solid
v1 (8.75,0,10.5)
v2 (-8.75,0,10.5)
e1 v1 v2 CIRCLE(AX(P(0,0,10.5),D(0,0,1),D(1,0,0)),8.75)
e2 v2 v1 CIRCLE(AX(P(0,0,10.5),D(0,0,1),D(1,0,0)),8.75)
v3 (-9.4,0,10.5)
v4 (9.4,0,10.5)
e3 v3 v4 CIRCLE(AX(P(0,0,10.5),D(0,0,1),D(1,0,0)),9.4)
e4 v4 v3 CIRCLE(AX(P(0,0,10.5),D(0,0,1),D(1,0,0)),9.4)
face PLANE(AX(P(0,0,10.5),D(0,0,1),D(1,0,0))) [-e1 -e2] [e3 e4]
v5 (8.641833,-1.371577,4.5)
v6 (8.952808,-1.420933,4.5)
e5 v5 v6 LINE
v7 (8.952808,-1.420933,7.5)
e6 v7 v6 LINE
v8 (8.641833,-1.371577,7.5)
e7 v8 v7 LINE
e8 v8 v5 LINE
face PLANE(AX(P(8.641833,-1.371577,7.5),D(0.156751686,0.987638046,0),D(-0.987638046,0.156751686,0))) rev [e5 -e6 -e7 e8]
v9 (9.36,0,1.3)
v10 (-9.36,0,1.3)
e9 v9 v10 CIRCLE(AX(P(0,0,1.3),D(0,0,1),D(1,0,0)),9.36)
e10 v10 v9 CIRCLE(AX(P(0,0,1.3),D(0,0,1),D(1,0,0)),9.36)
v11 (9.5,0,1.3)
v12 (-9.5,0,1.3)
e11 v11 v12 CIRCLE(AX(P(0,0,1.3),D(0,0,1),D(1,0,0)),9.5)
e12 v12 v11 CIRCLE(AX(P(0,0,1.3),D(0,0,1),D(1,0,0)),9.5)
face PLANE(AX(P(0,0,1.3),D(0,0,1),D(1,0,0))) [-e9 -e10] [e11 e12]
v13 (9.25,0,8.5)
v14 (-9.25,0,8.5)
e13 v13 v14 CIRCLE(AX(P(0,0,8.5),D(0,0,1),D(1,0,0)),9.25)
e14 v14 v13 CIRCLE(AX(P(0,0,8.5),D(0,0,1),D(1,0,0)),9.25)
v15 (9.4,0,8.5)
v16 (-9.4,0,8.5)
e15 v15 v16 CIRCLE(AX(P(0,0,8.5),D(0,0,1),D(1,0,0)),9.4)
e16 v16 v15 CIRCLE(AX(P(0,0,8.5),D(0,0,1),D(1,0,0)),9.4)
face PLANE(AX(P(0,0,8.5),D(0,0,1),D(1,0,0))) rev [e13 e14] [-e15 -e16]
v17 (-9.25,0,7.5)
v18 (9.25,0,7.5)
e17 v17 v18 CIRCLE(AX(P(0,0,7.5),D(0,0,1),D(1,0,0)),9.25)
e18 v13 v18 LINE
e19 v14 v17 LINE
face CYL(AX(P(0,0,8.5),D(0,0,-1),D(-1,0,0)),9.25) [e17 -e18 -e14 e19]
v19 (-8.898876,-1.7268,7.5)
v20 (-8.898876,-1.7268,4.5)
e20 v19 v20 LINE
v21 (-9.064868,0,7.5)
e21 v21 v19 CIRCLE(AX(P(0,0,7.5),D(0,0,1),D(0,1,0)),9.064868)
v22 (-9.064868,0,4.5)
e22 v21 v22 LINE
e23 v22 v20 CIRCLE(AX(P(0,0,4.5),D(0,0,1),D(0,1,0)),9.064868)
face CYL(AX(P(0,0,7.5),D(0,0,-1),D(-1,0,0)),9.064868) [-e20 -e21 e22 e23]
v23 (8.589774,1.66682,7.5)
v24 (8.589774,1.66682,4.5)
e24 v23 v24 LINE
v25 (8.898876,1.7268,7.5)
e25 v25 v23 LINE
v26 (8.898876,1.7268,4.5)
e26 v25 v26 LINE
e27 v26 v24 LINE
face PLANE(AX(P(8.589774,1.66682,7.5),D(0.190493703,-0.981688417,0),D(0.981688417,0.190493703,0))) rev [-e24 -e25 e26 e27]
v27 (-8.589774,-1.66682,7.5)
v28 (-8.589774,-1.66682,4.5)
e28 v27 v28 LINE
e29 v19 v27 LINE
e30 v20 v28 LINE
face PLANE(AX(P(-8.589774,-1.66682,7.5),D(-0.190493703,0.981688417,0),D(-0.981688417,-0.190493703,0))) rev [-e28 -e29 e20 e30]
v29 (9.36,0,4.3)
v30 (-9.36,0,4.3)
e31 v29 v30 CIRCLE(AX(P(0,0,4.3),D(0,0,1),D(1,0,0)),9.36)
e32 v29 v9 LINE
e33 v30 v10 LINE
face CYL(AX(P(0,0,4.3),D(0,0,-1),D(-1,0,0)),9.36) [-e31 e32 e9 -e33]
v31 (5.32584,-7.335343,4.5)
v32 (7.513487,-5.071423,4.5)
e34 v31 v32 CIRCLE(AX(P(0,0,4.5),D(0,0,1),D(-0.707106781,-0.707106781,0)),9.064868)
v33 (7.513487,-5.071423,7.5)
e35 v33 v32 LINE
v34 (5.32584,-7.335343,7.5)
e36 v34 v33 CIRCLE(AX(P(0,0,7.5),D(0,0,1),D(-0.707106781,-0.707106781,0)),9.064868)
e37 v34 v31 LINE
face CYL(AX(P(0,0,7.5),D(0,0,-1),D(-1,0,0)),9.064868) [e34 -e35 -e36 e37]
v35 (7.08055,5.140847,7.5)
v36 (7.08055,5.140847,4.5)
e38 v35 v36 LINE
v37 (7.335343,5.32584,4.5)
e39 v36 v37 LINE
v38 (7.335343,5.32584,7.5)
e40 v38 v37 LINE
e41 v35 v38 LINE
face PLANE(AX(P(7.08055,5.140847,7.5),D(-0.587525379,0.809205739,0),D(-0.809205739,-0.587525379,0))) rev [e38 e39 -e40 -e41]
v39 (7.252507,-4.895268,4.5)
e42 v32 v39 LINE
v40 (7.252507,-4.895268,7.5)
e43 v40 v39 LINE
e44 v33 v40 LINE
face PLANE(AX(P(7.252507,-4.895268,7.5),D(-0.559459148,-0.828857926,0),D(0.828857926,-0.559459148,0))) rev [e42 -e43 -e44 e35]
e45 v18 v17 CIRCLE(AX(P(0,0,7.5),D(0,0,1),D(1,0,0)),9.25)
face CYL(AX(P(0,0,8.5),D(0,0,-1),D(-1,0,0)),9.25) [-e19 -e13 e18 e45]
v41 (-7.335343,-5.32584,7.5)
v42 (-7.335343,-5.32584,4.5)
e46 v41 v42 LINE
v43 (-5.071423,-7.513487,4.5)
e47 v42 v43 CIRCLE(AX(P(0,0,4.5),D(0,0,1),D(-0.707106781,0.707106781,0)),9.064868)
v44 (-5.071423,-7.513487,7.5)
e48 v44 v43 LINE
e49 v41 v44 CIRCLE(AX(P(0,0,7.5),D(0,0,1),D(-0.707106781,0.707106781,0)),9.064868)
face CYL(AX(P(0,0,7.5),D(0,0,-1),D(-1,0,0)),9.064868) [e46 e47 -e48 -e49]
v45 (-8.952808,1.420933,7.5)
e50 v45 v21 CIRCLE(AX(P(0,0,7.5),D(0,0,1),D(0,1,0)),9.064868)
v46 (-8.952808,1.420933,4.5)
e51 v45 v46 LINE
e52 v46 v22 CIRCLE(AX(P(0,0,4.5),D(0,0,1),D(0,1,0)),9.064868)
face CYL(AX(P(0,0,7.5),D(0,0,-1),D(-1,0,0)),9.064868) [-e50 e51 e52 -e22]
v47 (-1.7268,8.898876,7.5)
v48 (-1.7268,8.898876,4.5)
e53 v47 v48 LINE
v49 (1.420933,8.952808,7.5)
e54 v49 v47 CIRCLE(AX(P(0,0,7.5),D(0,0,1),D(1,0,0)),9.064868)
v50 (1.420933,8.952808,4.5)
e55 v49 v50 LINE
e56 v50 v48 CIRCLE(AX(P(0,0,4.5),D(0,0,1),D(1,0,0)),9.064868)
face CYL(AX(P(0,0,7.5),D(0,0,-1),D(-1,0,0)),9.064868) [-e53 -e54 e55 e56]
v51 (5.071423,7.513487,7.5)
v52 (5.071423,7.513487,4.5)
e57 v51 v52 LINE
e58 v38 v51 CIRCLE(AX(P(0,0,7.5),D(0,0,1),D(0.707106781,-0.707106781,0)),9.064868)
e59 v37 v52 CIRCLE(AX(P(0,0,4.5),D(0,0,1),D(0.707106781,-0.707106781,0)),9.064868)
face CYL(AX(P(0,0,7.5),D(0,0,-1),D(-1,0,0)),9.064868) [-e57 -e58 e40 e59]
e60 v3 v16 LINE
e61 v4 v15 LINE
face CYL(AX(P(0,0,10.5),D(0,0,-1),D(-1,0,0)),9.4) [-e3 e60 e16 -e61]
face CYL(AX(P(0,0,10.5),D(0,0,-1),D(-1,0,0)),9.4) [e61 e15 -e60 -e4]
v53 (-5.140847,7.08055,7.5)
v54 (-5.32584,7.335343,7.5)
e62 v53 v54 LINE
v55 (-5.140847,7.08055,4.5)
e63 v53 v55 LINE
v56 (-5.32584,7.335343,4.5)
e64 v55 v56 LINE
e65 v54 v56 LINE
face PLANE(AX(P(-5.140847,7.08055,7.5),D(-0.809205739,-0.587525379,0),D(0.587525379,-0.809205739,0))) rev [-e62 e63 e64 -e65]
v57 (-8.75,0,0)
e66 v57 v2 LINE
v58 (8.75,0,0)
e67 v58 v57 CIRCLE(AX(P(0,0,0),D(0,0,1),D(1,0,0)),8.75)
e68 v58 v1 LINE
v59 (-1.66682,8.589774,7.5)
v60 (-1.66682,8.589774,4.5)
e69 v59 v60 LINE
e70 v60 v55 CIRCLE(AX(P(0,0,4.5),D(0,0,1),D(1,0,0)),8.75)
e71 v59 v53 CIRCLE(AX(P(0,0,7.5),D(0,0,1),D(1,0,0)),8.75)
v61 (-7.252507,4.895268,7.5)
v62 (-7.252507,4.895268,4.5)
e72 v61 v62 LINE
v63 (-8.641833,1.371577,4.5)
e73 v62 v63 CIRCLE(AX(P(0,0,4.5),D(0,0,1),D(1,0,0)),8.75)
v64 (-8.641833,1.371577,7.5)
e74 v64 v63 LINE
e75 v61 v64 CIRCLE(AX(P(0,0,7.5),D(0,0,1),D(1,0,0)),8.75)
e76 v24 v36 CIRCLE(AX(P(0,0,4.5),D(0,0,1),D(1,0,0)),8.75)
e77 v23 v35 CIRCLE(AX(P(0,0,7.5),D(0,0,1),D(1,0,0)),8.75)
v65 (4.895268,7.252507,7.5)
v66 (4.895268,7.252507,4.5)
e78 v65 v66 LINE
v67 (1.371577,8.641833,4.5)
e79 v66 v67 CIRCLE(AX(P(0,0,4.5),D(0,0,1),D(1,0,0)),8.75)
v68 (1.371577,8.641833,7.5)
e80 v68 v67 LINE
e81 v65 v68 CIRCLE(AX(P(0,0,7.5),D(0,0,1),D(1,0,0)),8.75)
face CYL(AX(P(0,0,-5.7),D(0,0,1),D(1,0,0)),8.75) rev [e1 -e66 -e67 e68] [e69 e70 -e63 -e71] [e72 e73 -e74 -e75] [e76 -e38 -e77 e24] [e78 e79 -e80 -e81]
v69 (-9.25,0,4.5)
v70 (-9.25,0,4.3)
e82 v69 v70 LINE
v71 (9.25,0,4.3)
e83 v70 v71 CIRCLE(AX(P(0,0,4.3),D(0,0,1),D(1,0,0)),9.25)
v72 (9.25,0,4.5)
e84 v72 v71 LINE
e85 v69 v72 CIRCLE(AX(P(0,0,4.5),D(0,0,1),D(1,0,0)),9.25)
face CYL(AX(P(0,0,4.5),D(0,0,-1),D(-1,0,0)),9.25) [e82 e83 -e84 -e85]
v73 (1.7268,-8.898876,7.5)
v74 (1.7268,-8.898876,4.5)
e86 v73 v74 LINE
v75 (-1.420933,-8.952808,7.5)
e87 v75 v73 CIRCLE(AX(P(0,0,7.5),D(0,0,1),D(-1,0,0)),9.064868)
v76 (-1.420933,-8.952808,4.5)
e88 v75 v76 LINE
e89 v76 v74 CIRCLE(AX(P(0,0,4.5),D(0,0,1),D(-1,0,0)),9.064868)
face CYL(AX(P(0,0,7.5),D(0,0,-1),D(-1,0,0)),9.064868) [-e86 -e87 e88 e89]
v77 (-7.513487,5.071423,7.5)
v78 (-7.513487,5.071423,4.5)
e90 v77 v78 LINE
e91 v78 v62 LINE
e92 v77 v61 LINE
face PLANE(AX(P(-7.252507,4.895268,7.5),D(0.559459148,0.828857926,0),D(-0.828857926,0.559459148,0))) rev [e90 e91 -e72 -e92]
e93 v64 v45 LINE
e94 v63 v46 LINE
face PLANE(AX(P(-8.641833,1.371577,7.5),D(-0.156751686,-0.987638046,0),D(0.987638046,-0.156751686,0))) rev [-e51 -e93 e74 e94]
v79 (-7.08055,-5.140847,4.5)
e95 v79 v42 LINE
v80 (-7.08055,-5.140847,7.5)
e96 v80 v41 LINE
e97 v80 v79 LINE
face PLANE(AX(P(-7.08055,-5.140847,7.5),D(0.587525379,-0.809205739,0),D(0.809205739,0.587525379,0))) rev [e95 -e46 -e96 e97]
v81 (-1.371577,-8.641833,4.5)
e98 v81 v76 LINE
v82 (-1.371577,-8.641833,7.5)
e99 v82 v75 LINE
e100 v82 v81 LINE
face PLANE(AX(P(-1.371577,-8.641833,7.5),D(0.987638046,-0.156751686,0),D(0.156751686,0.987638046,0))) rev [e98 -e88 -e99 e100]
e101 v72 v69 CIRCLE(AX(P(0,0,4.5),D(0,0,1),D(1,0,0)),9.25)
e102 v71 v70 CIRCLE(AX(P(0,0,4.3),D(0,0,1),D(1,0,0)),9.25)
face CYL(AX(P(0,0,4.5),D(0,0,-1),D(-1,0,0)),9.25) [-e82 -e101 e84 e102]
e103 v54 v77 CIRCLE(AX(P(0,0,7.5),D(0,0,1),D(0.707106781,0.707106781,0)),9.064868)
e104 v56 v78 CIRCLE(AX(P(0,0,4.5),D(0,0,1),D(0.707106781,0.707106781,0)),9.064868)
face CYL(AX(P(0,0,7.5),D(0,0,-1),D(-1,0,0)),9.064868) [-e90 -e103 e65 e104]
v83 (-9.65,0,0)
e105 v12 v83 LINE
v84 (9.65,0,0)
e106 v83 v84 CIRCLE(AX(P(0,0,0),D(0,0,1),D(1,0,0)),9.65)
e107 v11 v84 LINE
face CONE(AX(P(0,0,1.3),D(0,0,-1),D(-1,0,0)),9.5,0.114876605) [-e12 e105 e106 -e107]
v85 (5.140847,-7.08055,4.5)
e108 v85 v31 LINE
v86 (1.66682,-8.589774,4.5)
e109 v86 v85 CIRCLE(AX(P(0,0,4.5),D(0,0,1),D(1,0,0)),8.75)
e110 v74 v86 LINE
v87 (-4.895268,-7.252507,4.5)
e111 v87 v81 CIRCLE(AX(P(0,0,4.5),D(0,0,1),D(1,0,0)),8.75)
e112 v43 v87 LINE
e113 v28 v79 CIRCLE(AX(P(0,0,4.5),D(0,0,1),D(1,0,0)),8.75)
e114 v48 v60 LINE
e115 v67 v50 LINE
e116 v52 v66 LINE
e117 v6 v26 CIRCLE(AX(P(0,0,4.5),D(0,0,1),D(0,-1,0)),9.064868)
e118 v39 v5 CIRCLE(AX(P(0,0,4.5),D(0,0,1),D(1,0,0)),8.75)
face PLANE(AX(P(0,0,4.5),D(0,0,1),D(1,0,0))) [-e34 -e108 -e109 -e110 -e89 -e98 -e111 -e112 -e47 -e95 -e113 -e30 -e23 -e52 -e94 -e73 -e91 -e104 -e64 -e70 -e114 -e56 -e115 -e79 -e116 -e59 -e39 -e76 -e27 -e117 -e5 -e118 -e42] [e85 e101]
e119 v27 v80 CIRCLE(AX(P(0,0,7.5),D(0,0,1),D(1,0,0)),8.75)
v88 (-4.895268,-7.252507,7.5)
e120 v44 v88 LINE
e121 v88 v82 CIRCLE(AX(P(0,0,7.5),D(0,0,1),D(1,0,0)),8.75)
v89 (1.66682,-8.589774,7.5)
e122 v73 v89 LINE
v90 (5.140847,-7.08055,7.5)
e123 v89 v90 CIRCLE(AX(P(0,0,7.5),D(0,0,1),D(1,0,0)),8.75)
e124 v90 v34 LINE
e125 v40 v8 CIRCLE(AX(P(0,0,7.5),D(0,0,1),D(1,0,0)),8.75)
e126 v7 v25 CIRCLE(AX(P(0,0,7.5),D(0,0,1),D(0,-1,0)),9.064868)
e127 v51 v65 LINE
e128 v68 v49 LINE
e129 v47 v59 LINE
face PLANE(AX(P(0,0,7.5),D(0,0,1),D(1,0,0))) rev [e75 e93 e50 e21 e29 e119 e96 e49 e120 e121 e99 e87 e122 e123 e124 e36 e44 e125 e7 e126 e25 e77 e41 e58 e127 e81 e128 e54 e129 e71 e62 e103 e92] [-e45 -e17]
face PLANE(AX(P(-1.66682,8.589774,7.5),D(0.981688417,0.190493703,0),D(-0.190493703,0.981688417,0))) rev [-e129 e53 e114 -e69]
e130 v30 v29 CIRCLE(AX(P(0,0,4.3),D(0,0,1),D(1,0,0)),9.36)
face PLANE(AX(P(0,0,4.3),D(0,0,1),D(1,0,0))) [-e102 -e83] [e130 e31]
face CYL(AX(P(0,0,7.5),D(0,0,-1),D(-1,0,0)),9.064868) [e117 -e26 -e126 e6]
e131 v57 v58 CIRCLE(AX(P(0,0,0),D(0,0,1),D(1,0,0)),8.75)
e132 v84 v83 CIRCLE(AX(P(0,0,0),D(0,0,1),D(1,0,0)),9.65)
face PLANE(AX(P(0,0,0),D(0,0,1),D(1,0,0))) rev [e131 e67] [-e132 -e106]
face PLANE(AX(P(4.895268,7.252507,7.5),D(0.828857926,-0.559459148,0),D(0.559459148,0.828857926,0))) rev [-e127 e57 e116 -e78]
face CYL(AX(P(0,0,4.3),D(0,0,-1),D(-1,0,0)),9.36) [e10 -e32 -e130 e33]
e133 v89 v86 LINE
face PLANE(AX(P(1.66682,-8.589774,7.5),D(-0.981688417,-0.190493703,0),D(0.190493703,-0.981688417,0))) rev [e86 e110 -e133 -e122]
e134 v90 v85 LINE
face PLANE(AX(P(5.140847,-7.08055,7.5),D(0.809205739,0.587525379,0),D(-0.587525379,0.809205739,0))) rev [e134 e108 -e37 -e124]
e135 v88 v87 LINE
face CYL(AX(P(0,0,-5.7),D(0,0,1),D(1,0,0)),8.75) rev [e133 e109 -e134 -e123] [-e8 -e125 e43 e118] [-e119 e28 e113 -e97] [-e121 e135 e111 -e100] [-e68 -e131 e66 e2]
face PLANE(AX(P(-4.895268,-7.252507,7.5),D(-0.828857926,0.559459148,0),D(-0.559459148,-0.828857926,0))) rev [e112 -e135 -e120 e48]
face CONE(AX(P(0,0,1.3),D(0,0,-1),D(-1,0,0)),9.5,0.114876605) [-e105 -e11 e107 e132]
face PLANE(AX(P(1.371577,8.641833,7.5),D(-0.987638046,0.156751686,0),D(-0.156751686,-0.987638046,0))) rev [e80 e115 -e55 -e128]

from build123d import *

# Parameters (mm, degrees)
SKETCH1_R           = 9.65
SKETCH2_R           = 9.5
SKETCH3_R           = 9.36
BOSS_EXTRUDE1_DEPTH = 3
SKETCH4_R           = 9.25
BOSS_EXTRUDE2_DEPTH = 0.2
SKETCH5_R           = 8.75
CUT_EXTRUDE1_DEPTH  = 10.2
BOSS_EXTRUDE3_START = 3
BOSS_EXTRUDE3_DEPTH = 3
CIRPATTERN1_COUNT   = 8
SKETCH8_R           = 9.25
BOSS_EXTRUDE4_DEPTH = 1
SKETCH9_R           = 9.4
BOSS_EXTRUDE5_DEPTH = 2
SKETCH11_R          = 8.75
CUT_EXTRUDE2_DEPTH  = 9


with BuildPart() as part:
    # Sketch1 → Loft2 section 0
    with BuildSketch(Plane.XY):
        Circle(SKETCH1_R)
    # Sketch2 → Loft2 section 1
    with BuildSketch(Plane.XY.offset(1.3)):
        Circle(SKETCH2_R)
    loft()

    # Sketch3 → Boss-Extrude1 (add)
    with BuildSketch(Plane.XY.offset(1.3)):
        Circle(SKETCH3_R)
    extrude(amount=BOSS_EXTRUDE1_DEPTH)

    # Sketch4 → Boss-Extrude2 (add)
    with BuildSketch(Plane.XY.offset(4.3)):
        Circle(SKETCH4_R)
    extrude(amount=BOSS_EXTRUDE2_DEPTH)

    # Sketch5 → Cut-Extrude1 (cut)
    with BuildSketch(Plane.XY.offset(4.5)):
        Circle(SKETCH5_R)
    extrude(amount=-CUT_EXTRUDE1_DEPTH, mode=Mode.SUBTRACT)

    # Sketch7 → Boss-Extrude3 (add)
    with BuildSketch(Plane.XY.offset(4.5).offset(BOSS_EXTRUDE3_START)):
        with BuildLine():
            Line((-1.666819903, 8.589773653), (-1.726800204, 8.898875558))
            ThreePointArc((-1.726800204, 8.898875558), (-0.155292705, 9.063537352), (1.420933285, 8.952808149))
            Line((1.420933285, 8.952808149), (1.371577253, 8.641832898))
            ThreePointArc((1.371577253, 8.641832898), (-0.149898622, 8.748715929), (-1.666819903, 8.589773653))
        make_face()
    boss_extrude3 = extrude(amount=-BOSS_EXTRUDE3_DEPTH)

    # CirPattern1: Boss-Extrude3 ×8 about axis
    cirpattern1_axis = Axis((0, 0, 0), (0, 0, 1))
    for i in range(1, CIRPATTERN1_COUNT):
        add(boss_extrude3.rotate(cirpattern1_axis, i * 360 / CIRPATTERN1_COUNT))

    # Sketch8 → Boss-Extrude4 (add)
    with BuildSketch(Plane.XY.offset(7.5)):
        Circle(SKETCH8_R)
    extrude(amount=BOSS_EXTRUDE4_DEPTH)

    # Sketch9 → Boss-Extrude5 (add)
    with BuildSketch(Plane.XY.offset(8.5)):
        Circle(SKETCH9_R)
    extrude(amount=BOSS_EXTRUDE5_DEPTH)

    # Sketch11 → Cut-Extrude2 (cut)
    with BuildSketch(Plane.XY.offset(10.5)):
        Circle(SKETCH11_R)
    extrude(amount=-CUT_EXTRUDE2_DEPTH, mode=Mode.SUBTRACT)


solid = part.part
